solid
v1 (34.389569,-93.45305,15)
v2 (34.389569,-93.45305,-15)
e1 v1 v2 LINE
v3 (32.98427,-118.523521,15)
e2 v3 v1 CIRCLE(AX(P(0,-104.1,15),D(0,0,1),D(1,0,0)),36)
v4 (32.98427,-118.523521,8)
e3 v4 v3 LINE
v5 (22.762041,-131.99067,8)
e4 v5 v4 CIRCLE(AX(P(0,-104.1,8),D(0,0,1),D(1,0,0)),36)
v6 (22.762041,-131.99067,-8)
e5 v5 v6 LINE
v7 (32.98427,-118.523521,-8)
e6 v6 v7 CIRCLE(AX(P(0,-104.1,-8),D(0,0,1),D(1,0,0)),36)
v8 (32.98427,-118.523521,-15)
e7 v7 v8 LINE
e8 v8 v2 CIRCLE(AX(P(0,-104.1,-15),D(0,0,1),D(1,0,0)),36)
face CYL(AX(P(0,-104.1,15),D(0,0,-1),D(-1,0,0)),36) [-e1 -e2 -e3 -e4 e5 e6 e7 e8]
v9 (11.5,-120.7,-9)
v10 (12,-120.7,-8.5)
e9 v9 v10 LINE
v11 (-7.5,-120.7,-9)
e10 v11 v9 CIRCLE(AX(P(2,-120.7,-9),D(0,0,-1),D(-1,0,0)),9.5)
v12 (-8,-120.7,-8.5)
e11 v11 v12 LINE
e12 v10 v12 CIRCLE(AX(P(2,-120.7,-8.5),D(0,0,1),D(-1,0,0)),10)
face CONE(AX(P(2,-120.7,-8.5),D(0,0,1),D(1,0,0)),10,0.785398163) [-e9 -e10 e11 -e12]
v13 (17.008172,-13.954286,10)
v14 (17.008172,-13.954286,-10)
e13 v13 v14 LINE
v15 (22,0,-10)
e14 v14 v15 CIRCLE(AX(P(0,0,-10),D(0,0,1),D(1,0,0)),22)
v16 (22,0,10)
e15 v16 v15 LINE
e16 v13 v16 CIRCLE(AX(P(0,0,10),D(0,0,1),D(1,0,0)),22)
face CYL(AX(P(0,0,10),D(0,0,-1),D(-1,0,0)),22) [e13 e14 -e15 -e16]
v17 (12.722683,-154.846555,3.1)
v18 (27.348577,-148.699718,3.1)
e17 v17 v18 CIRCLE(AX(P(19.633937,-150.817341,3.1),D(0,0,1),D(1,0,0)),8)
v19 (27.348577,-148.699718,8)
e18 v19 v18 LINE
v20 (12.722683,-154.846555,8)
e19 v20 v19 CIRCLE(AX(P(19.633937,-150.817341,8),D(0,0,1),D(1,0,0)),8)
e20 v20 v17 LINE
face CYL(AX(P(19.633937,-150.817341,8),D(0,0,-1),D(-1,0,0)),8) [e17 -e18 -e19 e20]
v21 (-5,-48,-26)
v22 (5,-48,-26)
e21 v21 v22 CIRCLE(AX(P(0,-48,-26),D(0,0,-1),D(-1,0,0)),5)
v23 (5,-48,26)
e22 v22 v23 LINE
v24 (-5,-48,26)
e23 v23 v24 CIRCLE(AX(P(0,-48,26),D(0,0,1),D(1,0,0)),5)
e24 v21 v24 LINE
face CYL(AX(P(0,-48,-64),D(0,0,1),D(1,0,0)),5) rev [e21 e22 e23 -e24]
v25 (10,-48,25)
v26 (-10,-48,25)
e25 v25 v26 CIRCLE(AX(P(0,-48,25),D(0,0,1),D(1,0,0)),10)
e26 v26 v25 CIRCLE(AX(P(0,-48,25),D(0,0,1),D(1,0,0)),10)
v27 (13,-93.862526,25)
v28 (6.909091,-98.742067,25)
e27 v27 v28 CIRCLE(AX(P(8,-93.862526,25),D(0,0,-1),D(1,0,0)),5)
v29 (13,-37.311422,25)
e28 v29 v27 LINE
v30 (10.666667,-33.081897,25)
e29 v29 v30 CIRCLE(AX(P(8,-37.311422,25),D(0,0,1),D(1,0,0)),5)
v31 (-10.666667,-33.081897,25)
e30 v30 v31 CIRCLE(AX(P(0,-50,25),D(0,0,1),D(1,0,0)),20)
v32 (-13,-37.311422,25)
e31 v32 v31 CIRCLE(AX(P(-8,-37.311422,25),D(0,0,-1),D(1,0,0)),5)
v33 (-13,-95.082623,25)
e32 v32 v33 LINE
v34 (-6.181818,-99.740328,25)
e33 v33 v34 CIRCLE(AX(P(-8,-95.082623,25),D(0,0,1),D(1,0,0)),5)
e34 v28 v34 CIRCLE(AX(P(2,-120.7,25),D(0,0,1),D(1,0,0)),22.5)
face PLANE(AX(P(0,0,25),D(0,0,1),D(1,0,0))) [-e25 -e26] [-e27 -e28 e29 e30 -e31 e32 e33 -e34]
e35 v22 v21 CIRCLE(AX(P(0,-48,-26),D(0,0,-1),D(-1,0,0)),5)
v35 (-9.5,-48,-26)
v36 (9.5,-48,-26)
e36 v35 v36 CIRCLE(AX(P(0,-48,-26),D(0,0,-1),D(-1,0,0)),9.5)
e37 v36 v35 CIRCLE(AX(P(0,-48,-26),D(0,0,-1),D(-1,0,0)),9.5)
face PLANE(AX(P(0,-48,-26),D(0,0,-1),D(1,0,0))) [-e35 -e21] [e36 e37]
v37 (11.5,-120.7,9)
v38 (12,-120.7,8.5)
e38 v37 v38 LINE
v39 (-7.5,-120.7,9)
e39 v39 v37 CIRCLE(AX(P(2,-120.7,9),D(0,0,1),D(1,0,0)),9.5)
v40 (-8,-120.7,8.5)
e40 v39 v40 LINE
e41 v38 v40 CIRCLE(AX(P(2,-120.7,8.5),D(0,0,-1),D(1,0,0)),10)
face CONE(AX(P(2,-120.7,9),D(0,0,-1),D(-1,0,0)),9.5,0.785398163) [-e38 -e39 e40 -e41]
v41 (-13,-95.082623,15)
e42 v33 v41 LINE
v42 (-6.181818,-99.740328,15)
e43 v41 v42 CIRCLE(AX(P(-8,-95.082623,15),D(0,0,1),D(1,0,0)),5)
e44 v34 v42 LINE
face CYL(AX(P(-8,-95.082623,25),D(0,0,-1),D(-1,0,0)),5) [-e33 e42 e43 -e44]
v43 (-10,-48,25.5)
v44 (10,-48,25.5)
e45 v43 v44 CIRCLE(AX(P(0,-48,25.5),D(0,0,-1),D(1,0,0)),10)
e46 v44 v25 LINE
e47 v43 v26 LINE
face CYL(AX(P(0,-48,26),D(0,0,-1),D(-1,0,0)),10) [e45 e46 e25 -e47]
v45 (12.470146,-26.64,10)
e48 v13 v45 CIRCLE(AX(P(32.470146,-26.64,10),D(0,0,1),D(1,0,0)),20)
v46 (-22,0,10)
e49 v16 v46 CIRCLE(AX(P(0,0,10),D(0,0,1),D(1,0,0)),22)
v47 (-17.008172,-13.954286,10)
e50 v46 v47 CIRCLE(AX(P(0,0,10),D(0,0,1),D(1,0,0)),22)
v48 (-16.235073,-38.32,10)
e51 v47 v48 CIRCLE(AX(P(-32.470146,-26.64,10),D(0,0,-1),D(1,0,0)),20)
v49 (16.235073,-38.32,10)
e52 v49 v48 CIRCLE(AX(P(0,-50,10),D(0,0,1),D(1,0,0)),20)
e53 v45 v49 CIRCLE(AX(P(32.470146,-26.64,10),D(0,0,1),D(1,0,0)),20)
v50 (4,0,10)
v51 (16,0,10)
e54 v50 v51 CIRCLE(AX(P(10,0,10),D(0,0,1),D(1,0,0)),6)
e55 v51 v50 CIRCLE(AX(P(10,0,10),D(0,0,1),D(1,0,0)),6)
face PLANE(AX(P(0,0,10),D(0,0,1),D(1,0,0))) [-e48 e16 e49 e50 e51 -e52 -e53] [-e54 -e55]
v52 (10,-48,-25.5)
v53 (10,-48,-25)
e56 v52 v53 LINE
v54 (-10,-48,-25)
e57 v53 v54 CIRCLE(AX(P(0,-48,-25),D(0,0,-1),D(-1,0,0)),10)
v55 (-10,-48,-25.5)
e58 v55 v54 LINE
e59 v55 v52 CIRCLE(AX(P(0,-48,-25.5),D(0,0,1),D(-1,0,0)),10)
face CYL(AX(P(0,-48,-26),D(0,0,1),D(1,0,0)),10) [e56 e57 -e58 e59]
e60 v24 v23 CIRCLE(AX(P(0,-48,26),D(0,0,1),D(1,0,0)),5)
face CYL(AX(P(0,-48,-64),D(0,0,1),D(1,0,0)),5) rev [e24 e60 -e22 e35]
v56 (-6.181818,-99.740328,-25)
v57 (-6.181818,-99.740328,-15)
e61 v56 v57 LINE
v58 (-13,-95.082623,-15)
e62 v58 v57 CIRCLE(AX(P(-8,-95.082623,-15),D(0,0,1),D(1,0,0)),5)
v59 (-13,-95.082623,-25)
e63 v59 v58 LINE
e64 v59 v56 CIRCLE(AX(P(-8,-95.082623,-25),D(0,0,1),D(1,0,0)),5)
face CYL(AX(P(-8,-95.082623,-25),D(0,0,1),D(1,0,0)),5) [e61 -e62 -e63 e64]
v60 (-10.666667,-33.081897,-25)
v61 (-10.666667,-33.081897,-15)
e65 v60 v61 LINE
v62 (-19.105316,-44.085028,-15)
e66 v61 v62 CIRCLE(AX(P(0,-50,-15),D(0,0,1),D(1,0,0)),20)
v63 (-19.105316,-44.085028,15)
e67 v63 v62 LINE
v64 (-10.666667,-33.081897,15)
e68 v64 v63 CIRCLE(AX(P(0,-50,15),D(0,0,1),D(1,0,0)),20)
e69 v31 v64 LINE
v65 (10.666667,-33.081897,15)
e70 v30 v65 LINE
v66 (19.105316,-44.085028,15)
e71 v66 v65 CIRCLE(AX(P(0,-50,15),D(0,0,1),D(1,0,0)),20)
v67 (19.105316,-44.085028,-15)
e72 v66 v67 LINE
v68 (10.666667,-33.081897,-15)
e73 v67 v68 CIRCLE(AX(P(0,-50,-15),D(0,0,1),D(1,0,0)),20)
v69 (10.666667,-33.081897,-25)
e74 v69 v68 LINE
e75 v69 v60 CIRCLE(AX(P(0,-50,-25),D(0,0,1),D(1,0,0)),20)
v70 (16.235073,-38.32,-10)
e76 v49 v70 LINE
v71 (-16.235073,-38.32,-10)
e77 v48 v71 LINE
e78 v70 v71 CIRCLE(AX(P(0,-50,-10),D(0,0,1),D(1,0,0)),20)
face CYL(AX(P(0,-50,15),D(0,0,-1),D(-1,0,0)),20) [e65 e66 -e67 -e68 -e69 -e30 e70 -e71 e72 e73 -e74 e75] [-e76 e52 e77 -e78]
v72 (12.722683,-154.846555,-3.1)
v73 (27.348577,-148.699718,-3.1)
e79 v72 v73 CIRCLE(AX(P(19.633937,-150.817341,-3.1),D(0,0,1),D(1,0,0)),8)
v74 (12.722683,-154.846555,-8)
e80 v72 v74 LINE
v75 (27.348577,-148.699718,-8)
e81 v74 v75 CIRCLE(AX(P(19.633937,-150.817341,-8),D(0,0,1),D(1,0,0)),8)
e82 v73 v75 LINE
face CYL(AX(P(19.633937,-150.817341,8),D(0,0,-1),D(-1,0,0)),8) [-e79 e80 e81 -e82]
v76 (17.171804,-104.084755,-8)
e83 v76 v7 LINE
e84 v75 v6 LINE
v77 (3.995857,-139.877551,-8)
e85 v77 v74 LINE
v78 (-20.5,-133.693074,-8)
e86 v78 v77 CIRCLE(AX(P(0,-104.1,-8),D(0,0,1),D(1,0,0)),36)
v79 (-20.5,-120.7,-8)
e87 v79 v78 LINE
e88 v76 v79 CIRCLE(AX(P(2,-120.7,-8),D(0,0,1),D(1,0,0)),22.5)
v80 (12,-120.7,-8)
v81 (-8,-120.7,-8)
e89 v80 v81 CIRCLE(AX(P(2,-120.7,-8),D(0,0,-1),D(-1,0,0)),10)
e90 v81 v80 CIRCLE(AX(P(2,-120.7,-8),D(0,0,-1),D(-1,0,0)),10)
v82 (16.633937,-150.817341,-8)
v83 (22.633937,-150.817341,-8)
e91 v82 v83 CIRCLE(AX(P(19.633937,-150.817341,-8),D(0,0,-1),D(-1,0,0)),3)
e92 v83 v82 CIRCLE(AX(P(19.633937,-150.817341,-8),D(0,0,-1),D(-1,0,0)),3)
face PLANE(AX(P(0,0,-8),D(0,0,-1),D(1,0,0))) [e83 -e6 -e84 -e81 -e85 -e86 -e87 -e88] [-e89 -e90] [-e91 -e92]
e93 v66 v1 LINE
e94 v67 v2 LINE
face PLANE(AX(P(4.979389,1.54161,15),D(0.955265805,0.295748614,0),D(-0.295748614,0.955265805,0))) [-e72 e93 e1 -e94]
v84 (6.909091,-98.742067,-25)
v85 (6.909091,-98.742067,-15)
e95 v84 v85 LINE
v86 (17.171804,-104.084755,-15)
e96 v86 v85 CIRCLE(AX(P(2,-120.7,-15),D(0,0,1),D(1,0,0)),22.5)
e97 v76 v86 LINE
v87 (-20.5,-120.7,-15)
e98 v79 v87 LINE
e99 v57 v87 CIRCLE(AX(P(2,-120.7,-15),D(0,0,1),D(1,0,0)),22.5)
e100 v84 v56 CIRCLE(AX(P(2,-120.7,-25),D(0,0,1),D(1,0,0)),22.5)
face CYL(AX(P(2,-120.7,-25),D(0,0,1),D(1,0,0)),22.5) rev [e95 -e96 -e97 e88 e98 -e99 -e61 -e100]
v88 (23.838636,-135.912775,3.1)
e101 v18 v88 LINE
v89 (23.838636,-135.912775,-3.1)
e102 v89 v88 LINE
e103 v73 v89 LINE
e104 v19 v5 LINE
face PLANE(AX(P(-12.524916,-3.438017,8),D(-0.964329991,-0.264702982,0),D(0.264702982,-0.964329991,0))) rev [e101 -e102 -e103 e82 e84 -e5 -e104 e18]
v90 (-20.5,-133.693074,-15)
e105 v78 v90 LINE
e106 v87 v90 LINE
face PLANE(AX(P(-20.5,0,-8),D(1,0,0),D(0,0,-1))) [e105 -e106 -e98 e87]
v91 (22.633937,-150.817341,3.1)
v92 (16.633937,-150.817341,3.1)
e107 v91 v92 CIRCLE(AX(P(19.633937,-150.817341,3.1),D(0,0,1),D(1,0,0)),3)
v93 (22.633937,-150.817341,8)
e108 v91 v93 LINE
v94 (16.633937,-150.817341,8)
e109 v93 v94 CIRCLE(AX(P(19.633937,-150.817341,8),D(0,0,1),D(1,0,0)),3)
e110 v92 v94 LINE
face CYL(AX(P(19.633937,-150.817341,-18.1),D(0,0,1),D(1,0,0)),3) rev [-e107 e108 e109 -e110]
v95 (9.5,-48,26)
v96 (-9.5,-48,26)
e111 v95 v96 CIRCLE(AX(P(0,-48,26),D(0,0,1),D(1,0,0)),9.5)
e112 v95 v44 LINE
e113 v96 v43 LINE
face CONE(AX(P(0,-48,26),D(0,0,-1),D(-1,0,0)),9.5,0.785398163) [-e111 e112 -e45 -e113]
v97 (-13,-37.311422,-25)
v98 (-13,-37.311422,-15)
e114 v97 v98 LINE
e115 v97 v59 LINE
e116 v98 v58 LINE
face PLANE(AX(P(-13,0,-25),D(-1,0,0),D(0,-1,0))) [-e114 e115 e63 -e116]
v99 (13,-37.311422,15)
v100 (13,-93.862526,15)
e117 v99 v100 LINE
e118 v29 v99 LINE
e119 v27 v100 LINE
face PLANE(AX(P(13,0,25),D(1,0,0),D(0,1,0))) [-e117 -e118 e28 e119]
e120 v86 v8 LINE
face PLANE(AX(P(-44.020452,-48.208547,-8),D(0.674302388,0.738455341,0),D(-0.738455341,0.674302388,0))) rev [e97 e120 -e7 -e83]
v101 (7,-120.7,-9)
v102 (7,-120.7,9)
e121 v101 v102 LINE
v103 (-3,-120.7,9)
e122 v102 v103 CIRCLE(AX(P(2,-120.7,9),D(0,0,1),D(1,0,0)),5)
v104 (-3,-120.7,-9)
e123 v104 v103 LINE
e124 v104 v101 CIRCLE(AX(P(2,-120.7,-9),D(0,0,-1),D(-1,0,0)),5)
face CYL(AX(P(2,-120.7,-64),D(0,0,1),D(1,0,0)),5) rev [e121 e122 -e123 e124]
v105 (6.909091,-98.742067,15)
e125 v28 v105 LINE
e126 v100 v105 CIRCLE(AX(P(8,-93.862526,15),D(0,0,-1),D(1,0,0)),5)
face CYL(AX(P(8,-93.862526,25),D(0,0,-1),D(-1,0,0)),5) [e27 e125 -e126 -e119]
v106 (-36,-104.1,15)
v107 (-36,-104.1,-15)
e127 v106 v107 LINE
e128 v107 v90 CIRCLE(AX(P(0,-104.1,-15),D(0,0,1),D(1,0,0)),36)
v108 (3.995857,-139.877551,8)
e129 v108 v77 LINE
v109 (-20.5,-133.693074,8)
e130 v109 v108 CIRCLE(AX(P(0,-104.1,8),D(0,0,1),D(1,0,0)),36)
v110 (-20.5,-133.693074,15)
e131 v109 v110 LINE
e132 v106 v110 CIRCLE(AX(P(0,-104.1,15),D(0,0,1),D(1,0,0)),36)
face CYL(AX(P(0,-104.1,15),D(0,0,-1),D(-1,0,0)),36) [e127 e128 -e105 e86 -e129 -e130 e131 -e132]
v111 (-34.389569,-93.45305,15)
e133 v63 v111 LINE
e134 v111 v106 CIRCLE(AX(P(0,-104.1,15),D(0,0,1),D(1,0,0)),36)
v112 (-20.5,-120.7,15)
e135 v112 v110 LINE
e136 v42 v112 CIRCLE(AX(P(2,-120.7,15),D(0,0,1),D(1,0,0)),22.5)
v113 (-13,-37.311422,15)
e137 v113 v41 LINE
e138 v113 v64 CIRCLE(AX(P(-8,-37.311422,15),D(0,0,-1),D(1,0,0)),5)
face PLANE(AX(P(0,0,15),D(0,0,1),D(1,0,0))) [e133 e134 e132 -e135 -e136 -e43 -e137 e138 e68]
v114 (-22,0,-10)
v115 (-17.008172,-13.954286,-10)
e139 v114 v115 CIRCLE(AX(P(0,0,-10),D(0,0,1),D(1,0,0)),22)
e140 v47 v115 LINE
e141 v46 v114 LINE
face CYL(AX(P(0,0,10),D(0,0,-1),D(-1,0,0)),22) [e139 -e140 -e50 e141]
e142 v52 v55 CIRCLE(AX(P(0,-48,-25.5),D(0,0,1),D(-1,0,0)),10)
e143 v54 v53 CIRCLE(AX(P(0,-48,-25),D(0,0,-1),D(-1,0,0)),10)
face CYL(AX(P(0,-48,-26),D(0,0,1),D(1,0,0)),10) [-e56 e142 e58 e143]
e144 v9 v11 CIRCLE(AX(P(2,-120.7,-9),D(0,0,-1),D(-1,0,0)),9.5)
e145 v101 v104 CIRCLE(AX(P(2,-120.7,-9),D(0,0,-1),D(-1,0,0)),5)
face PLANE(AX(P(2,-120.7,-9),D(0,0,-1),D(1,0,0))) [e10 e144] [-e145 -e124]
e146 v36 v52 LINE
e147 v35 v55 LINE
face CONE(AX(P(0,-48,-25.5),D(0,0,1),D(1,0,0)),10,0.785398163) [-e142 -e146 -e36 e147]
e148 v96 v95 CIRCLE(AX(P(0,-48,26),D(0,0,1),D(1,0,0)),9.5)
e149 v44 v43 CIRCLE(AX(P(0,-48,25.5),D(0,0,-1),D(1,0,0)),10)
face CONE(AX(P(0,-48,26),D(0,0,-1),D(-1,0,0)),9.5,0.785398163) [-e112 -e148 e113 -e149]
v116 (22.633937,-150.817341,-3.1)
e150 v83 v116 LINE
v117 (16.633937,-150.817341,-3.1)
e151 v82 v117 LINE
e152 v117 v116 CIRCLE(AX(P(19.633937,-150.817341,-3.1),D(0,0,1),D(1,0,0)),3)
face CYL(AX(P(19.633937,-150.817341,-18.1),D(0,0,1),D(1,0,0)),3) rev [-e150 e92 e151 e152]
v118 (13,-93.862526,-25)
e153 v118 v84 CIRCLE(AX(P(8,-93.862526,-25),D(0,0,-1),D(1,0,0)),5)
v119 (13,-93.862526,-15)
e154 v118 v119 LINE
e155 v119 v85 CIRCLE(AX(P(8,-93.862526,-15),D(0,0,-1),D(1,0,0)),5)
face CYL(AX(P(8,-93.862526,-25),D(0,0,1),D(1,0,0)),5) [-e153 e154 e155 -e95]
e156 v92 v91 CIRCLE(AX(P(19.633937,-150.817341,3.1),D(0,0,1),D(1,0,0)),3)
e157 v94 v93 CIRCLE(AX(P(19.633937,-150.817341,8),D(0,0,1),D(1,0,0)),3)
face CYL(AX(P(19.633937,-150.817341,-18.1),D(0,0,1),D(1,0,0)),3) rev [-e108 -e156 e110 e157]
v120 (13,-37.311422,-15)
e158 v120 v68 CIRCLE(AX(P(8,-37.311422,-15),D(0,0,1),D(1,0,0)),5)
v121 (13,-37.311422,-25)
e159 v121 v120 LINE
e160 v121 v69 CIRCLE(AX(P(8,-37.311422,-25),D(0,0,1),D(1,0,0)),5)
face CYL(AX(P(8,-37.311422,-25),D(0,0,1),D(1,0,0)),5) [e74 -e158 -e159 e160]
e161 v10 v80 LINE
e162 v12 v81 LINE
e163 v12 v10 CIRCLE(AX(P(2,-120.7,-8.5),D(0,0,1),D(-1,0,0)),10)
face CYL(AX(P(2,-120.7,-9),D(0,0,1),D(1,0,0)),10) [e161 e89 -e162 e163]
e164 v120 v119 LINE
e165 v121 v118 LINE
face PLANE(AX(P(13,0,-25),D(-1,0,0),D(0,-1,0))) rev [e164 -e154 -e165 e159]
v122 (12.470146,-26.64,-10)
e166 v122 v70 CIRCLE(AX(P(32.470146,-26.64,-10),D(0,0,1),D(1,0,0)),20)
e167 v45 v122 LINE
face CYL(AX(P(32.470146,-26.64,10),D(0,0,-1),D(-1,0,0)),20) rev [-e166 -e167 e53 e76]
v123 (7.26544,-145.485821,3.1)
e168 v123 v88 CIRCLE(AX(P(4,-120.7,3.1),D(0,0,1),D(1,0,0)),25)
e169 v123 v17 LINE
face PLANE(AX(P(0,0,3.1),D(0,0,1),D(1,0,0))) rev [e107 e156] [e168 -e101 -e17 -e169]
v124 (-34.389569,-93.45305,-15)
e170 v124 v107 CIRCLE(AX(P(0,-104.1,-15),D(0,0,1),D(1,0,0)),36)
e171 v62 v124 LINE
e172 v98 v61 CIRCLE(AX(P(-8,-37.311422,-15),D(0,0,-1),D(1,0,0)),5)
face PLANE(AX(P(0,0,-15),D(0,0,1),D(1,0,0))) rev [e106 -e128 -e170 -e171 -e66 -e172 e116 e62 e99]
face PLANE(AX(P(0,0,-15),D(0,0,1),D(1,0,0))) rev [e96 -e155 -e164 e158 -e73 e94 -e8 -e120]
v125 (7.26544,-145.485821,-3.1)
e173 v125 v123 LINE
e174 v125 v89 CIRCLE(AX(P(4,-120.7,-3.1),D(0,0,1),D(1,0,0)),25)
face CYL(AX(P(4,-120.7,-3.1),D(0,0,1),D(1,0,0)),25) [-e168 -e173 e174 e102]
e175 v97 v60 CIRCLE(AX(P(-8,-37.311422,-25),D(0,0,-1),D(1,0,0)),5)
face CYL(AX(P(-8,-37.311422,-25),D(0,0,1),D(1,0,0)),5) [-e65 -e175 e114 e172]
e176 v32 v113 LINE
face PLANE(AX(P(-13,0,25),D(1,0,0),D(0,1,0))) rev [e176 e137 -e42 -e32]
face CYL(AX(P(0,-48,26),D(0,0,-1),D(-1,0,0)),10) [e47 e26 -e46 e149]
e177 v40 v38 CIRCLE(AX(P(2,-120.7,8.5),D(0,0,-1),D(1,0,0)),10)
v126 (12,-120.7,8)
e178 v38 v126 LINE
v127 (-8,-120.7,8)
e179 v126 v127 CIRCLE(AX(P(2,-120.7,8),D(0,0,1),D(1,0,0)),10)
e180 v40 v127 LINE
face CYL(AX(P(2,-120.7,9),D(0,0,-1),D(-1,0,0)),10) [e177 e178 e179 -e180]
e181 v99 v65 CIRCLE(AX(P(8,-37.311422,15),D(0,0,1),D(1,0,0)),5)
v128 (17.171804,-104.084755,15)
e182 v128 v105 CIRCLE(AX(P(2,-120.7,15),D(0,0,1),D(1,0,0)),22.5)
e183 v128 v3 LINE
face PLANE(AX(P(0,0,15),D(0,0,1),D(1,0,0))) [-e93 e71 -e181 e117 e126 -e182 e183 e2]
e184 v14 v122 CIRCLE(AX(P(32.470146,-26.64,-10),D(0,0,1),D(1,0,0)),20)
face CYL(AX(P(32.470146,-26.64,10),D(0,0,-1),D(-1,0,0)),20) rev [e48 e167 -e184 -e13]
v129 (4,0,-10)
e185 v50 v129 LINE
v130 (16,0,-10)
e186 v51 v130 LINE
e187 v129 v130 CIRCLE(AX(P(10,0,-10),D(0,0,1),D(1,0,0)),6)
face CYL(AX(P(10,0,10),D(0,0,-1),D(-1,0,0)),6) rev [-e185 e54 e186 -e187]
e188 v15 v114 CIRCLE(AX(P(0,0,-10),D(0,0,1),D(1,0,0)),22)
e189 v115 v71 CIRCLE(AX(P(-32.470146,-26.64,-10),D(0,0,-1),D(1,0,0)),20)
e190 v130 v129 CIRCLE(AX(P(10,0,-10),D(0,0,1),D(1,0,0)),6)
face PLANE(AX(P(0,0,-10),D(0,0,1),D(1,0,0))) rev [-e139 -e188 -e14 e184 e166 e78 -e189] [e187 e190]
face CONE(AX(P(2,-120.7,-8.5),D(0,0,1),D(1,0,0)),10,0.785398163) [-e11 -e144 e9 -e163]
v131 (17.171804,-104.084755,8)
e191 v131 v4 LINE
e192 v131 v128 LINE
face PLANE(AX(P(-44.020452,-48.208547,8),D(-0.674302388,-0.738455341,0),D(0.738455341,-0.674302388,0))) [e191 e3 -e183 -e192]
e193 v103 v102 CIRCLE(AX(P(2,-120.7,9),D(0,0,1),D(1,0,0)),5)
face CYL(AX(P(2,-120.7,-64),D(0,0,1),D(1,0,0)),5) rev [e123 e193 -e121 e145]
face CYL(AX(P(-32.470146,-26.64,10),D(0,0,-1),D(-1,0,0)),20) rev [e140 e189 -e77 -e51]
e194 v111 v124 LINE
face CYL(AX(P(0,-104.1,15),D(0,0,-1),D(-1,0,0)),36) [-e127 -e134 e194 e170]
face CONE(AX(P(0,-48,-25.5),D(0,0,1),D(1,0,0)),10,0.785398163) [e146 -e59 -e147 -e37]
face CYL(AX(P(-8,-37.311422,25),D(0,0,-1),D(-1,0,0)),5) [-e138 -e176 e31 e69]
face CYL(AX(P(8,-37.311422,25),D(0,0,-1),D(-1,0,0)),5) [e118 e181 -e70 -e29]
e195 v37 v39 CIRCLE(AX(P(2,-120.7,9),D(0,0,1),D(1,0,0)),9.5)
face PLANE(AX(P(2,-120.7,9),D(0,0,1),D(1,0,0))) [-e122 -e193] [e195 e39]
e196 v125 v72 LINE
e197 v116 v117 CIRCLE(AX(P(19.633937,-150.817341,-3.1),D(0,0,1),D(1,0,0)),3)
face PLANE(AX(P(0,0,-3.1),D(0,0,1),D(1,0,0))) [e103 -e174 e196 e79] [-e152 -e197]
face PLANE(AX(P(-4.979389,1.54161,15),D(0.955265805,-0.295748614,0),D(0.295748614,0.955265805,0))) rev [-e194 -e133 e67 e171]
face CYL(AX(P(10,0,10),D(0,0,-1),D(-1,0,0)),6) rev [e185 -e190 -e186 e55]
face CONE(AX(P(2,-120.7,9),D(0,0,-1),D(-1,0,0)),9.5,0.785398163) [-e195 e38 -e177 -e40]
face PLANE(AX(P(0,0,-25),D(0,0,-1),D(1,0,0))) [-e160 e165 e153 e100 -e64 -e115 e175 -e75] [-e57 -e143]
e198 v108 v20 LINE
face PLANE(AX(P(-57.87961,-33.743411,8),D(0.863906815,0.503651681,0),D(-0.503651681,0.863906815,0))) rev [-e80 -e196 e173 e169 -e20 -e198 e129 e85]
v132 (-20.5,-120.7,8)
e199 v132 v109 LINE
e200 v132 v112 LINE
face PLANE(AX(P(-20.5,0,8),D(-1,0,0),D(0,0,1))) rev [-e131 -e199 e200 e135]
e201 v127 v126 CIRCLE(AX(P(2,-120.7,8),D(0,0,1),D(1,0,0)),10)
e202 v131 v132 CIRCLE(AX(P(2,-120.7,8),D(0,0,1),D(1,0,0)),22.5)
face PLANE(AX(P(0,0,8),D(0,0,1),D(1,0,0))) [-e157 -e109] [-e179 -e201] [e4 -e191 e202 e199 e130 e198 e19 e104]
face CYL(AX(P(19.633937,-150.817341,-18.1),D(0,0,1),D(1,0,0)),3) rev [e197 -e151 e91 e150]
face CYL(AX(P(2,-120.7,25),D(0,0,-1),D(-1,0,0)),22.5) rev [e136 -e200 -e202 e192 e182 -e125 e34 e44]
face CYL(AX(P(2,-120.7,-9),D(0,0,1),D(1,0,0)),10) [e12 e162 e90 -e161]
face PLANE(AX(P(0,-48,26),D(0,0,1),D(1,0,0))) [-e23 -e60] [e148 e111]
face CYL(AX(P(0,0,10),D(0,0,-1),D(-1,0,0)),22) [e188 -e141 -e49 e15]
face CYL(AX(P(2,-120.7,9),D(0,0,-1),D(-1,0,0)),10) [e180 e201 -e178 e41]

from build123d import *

# Parameters (mm, degrees)
SKETCH_1_3_R             = 6
BOSS_EXTRUDE1_DEPTH      = 10
BOSS_EXTRUDE2_DEPTH      = 15
BOSS_EXTRUDE3_START      = 10
BOSS_EXTRUDE3_DEPTH      = 10
CUT_EXTRUDE1_DEPTH       = 7
SKETCH4_R                = 10
BOSS_EXTRUDE4_DEPTH      = 1
CHAMFER1_SIZE            = 0.5
SKETCH5_R                = 10
BOSS_EXTRUDE5_DEPTH      = 1
CHAMFER2_SIZE            = 0.5
CHAMFER1_OF_MIRROR2_SIZE = 0.5
CHAMFER2_OF_MIRROR2_SIZE = 0.5
SKETCH6_R                = 5
CUT_EXTRUDE3_DEPTH       = 90
BOSS_EXTRUDE7_DEPTH      = 8
CUT_EXTRUDE4_DEPTH       = 3.1
SKETCH8_R                = 3
CUT_EXTRUDE5_DEPTH       = 26.1


with BuildPart() as part:
    # Sketch 1_3 → Boss-Extrude1 (new, symmetric)
    with BuildSketch(Plane.XY):
        with BuildLine():
            ThreePointArc((-17.008171865, -13.954285714), (-12.480205961, -26.005740026), (-16.235073144, -38.32))
            ThreePointArc((-16.235073144, -38.32), (0, -30), (16.235073144, -38.32))
            ThreePointArc((16.235073144, -38.32), (12.480205961, -26.005740026), (17.008171865, -13.954285714))
            ThreePointArc((17.008171865, -13.954285714), (0, 22), (-17.008171865, -13.954285714))
        make_face()
        with Locations((10, 0)):
            Circle(SKETCH_1_3_R, mode=Mode.SUBTRACT)
    extrude(amount=BOSS_EXTRUDE1_DEPTH, both=True)

    # Sketch 1_3 2 → Boss-Extrude2 (add, symmetric)
    with BuildSketch(Plane.XY):
        with BuildLine():
            Line((-19.105316093, -44.085027726), (-34.389568967, -93.453049908))
            ThreePointArc((-34.389568967, -93.453049908), (0, -140.1), (34.389568967, -93.453049908))
            Line((34.389568967, -93.453049908), (19.105316093, -44.085027726))
            ThreePointArc((19.105316093, -44.085027726), (0, -30), (-19.105316093, -44.085027726))
        make_face()
    extrude(amount=BOSS_EXTRUDE2_DEPTH, both=True)

    # Sketch 3_4 → Boss-Extrude3 (add)
    with BuildSketch(Plane.XY.offset(15).offset(BOSS_EXTRUDE3_START)):
        with BuildLine():
            ThreePointArc((-10.666666667, -33.081896613), (-12.377975179, -34.896193002), (-13, -37.31142246))
            Line((-13, -37.31142246), (-13, -95.082623085))
            ThreePointArc((-13, -95.082623085), (-10.820380374, -99.211237204), (-6.181818182, -99.740327979))
            ThreePointArc((-6.181818182, -99.740327979), (0.289205667, -98.265134662), (6.909090909, -98.74206689))
            ThreePointArc((6.909090909, -98.74206689), (11.126136157, -97.764740023), (13, -93.862526199))
            Line((13, -93.862526199), (13, -37.31142246))
            ThreePointArc((13, -37.31142246), (12.377975179, -34.896193002), (10.666666667, -33.081896613))
            ThreePointArc((10.666666667, -33.081896613), (0, -30), (-10.666666667, -33.081896613))
        make_face()
    boss_extrude3 = extrude(amount=-BOSS_EXTRUDE3_DEPTH)

    # Sketch 3_4 2 → Cut-Extrude1 (cut)
    with BuildSketch(Plane.XY.offset(15)):
        with BuildLine():
            ThreePointArc((6.909090909, -98.74206689), (0.289205667, -98.265134662), (-6.181818182, -99.740327979))
            ThreePointArc((-6.181818182, -99.740327979), (-16.578763537, -108.008288317), (-20.5, -120.7))
            Line((-20.5, -120.7), (-20.5, -133.693073514))
            ThreePointArc((-20.5, -133.693073514), (9.82308926, -138.733898386), (32.984269817, -118.523520535))
            Line((32.984269817, -118.523520535), (17.171803721, -104.084754836))
            ThreePointArc((17.171803721, -104.084754836), (12.38973825, -100.742461597), (6.909090909, -98.74206689))
        make_face()
    cut_extrude1 = extrude(amount=-CUT_EXTRUDE1_DEPTH, mode=Mode.SUBTRACT)

    # Mirror1: Boss-Extrude3, Cut-Extrude1 across plane
    add(boss_extrude3.mirror(Plane.XY))
    add(cut_extrude1.mirror(Plane.XY), mode=Mode.SUBTRACT)

    # Sketch4 → Boss-Extrude4 (add)
    with BuildSketch(Plane.XY.offset(25)):
        with Locations((0, -48)):
            Circle(SKETCH4_R)
    boss_extrude4 = extrude(amount=BOSS_EXTRUDE4_DEPTH)

    # Chamfer1
    chamfer1_edges = [part.edges().sort_by_distance(p)[0] for p in [
        (-10, -48, 26),
    ]]
    chamfer(chamfer1_edges, length=CHAMFER1_SIZE)

    # Sketch5 → Boss-Extrude5 (add)
    with BuildSketch(Plane.XY.offset(8)):
        with Locations((2, -120.7)):
            Circle(SKETCH5_R)
    boss_extrude5 = extrude(amount=BOSS_EXTRUDE5_DEPTH)

    # Chamfer2
    chamfer2_edges = [part.edges().sort_by_distance(p)[0] for p in [
        (-8, -120.7, 9),
    ]]
    chamfer(chamfer2_edges, length=CHAMFER2_SIZE)

    # Mirror2: Boss-Extrude4, Boss-Extrude5 across plane
    add(boss_extrude4.mirror(Plane.XY))
    add(boss_extrude5.mirror(Plane.XY))

    # Chamfer1 of Mirror2
    chamfer1_of_mirror2_edges = [part.edges().sort_by_distance(p)[0] for p in [
        (-10, -48, -26),
    ]]
    chamfer(chamfer1_of_mirror2_edges, length=CHAMFER1_OF_MIRROR2_SIZE)

    # Chamfer2 of Mirror2
    chamfer2_of_mirror2_edges = [part.edges().sort_by_distance(p)[0] for p in [
        (-8, -120.7, -9),
    ]]
    chamfer(chamfer2_of_mirror2_edges, length=CHAMFER2_OF_MIRROR2_SIZE)

    # Sketch6 → Cut-Extrude3 (cut)
    with BuildSketch(Plane.XY.offset(26)):
        with Locations((0, -48)):
            Circle(SKETCH6_R)
        with Locations((2, -120.7)):
            Circle(SKETCH6_R)
    extrude(amount=-CUT_EXTRUDE3_DEPTH, mode=Mode.SUBTRACT)

    # Sketch 7_4 → Boss-Extrude7 (add, symmetric)
    with BuildSketch(Plane.XY):
        with BuildLine():
            ThreePointArc((7.265439801, -145.485820602), (16.504414385, -142.348085848), (23.838635926, -135.912775046))
            Line((23.838635926, -135.912775046), (22.762040961, -131.990670327))
            ThreePointArc((22.762040961, -131.990670327), (13.94801059, -137.288145483), (3.995857269, -139.877550569))
            Line((3.995857269, -139.877550569), (7.265439801, -145.485820602))
        make_face()
        with BuildLine():
            ThreePointArc((12.722682919, -154.846554807), (22.733495344, -158.1924848), (27.348577363, -148.699717507))
            Line((27.348577363, -148.699717507), (23.838635926, -135.912775046))
            ThreePointArc((23.838635926, -135.912775046), (16.504414385, -142.348085848), (7.265439801, -145.485820602))
            Line((7.265439801, -145.485820602), (12.722682919, -154.846554807))
        make_face()
    extrude(amount=BOSS_EXTRUDE7_DEPTH, both=True)

    # Sketch 7_4 2 → Cut-Extrude4 (cut, symmetric)
    with BuildSketch(Plane.XY):
        with BuildLine():
            ThreePointArc((12.722682919, -154.846554807), (22.733495344, -158.1924848), (27.348577363, -148.699717507))
            Line((27.348577363, -148.699717507), (23.838635926, -135.912775046))
            ThreePointArc((23.838635926, -135.912775046), (16.504414385, -142.348085848), (7.265439801, -145.485820602))
            Line((7.265439801, -145.485820602), (12.722682919, -154.846554807))
        make_face()
    extrude(amount=CUT_EXTRUDE4_DEPTH, both=True, mode=Mode.SUBTRACT)

    # Sketch8 → Cut-Extrude5 (cut, symmetric)
    with BuildSketch(Plane.XY.offset(8)):
        with Locations((19.633937435, -150.817341359)):
            Circle(SKETCH8_R)
    extrude(amount=CUT_EXTRUDE5_DEPTH, both=True, mode=Mode.SUBTRACT)


solid = part.part
